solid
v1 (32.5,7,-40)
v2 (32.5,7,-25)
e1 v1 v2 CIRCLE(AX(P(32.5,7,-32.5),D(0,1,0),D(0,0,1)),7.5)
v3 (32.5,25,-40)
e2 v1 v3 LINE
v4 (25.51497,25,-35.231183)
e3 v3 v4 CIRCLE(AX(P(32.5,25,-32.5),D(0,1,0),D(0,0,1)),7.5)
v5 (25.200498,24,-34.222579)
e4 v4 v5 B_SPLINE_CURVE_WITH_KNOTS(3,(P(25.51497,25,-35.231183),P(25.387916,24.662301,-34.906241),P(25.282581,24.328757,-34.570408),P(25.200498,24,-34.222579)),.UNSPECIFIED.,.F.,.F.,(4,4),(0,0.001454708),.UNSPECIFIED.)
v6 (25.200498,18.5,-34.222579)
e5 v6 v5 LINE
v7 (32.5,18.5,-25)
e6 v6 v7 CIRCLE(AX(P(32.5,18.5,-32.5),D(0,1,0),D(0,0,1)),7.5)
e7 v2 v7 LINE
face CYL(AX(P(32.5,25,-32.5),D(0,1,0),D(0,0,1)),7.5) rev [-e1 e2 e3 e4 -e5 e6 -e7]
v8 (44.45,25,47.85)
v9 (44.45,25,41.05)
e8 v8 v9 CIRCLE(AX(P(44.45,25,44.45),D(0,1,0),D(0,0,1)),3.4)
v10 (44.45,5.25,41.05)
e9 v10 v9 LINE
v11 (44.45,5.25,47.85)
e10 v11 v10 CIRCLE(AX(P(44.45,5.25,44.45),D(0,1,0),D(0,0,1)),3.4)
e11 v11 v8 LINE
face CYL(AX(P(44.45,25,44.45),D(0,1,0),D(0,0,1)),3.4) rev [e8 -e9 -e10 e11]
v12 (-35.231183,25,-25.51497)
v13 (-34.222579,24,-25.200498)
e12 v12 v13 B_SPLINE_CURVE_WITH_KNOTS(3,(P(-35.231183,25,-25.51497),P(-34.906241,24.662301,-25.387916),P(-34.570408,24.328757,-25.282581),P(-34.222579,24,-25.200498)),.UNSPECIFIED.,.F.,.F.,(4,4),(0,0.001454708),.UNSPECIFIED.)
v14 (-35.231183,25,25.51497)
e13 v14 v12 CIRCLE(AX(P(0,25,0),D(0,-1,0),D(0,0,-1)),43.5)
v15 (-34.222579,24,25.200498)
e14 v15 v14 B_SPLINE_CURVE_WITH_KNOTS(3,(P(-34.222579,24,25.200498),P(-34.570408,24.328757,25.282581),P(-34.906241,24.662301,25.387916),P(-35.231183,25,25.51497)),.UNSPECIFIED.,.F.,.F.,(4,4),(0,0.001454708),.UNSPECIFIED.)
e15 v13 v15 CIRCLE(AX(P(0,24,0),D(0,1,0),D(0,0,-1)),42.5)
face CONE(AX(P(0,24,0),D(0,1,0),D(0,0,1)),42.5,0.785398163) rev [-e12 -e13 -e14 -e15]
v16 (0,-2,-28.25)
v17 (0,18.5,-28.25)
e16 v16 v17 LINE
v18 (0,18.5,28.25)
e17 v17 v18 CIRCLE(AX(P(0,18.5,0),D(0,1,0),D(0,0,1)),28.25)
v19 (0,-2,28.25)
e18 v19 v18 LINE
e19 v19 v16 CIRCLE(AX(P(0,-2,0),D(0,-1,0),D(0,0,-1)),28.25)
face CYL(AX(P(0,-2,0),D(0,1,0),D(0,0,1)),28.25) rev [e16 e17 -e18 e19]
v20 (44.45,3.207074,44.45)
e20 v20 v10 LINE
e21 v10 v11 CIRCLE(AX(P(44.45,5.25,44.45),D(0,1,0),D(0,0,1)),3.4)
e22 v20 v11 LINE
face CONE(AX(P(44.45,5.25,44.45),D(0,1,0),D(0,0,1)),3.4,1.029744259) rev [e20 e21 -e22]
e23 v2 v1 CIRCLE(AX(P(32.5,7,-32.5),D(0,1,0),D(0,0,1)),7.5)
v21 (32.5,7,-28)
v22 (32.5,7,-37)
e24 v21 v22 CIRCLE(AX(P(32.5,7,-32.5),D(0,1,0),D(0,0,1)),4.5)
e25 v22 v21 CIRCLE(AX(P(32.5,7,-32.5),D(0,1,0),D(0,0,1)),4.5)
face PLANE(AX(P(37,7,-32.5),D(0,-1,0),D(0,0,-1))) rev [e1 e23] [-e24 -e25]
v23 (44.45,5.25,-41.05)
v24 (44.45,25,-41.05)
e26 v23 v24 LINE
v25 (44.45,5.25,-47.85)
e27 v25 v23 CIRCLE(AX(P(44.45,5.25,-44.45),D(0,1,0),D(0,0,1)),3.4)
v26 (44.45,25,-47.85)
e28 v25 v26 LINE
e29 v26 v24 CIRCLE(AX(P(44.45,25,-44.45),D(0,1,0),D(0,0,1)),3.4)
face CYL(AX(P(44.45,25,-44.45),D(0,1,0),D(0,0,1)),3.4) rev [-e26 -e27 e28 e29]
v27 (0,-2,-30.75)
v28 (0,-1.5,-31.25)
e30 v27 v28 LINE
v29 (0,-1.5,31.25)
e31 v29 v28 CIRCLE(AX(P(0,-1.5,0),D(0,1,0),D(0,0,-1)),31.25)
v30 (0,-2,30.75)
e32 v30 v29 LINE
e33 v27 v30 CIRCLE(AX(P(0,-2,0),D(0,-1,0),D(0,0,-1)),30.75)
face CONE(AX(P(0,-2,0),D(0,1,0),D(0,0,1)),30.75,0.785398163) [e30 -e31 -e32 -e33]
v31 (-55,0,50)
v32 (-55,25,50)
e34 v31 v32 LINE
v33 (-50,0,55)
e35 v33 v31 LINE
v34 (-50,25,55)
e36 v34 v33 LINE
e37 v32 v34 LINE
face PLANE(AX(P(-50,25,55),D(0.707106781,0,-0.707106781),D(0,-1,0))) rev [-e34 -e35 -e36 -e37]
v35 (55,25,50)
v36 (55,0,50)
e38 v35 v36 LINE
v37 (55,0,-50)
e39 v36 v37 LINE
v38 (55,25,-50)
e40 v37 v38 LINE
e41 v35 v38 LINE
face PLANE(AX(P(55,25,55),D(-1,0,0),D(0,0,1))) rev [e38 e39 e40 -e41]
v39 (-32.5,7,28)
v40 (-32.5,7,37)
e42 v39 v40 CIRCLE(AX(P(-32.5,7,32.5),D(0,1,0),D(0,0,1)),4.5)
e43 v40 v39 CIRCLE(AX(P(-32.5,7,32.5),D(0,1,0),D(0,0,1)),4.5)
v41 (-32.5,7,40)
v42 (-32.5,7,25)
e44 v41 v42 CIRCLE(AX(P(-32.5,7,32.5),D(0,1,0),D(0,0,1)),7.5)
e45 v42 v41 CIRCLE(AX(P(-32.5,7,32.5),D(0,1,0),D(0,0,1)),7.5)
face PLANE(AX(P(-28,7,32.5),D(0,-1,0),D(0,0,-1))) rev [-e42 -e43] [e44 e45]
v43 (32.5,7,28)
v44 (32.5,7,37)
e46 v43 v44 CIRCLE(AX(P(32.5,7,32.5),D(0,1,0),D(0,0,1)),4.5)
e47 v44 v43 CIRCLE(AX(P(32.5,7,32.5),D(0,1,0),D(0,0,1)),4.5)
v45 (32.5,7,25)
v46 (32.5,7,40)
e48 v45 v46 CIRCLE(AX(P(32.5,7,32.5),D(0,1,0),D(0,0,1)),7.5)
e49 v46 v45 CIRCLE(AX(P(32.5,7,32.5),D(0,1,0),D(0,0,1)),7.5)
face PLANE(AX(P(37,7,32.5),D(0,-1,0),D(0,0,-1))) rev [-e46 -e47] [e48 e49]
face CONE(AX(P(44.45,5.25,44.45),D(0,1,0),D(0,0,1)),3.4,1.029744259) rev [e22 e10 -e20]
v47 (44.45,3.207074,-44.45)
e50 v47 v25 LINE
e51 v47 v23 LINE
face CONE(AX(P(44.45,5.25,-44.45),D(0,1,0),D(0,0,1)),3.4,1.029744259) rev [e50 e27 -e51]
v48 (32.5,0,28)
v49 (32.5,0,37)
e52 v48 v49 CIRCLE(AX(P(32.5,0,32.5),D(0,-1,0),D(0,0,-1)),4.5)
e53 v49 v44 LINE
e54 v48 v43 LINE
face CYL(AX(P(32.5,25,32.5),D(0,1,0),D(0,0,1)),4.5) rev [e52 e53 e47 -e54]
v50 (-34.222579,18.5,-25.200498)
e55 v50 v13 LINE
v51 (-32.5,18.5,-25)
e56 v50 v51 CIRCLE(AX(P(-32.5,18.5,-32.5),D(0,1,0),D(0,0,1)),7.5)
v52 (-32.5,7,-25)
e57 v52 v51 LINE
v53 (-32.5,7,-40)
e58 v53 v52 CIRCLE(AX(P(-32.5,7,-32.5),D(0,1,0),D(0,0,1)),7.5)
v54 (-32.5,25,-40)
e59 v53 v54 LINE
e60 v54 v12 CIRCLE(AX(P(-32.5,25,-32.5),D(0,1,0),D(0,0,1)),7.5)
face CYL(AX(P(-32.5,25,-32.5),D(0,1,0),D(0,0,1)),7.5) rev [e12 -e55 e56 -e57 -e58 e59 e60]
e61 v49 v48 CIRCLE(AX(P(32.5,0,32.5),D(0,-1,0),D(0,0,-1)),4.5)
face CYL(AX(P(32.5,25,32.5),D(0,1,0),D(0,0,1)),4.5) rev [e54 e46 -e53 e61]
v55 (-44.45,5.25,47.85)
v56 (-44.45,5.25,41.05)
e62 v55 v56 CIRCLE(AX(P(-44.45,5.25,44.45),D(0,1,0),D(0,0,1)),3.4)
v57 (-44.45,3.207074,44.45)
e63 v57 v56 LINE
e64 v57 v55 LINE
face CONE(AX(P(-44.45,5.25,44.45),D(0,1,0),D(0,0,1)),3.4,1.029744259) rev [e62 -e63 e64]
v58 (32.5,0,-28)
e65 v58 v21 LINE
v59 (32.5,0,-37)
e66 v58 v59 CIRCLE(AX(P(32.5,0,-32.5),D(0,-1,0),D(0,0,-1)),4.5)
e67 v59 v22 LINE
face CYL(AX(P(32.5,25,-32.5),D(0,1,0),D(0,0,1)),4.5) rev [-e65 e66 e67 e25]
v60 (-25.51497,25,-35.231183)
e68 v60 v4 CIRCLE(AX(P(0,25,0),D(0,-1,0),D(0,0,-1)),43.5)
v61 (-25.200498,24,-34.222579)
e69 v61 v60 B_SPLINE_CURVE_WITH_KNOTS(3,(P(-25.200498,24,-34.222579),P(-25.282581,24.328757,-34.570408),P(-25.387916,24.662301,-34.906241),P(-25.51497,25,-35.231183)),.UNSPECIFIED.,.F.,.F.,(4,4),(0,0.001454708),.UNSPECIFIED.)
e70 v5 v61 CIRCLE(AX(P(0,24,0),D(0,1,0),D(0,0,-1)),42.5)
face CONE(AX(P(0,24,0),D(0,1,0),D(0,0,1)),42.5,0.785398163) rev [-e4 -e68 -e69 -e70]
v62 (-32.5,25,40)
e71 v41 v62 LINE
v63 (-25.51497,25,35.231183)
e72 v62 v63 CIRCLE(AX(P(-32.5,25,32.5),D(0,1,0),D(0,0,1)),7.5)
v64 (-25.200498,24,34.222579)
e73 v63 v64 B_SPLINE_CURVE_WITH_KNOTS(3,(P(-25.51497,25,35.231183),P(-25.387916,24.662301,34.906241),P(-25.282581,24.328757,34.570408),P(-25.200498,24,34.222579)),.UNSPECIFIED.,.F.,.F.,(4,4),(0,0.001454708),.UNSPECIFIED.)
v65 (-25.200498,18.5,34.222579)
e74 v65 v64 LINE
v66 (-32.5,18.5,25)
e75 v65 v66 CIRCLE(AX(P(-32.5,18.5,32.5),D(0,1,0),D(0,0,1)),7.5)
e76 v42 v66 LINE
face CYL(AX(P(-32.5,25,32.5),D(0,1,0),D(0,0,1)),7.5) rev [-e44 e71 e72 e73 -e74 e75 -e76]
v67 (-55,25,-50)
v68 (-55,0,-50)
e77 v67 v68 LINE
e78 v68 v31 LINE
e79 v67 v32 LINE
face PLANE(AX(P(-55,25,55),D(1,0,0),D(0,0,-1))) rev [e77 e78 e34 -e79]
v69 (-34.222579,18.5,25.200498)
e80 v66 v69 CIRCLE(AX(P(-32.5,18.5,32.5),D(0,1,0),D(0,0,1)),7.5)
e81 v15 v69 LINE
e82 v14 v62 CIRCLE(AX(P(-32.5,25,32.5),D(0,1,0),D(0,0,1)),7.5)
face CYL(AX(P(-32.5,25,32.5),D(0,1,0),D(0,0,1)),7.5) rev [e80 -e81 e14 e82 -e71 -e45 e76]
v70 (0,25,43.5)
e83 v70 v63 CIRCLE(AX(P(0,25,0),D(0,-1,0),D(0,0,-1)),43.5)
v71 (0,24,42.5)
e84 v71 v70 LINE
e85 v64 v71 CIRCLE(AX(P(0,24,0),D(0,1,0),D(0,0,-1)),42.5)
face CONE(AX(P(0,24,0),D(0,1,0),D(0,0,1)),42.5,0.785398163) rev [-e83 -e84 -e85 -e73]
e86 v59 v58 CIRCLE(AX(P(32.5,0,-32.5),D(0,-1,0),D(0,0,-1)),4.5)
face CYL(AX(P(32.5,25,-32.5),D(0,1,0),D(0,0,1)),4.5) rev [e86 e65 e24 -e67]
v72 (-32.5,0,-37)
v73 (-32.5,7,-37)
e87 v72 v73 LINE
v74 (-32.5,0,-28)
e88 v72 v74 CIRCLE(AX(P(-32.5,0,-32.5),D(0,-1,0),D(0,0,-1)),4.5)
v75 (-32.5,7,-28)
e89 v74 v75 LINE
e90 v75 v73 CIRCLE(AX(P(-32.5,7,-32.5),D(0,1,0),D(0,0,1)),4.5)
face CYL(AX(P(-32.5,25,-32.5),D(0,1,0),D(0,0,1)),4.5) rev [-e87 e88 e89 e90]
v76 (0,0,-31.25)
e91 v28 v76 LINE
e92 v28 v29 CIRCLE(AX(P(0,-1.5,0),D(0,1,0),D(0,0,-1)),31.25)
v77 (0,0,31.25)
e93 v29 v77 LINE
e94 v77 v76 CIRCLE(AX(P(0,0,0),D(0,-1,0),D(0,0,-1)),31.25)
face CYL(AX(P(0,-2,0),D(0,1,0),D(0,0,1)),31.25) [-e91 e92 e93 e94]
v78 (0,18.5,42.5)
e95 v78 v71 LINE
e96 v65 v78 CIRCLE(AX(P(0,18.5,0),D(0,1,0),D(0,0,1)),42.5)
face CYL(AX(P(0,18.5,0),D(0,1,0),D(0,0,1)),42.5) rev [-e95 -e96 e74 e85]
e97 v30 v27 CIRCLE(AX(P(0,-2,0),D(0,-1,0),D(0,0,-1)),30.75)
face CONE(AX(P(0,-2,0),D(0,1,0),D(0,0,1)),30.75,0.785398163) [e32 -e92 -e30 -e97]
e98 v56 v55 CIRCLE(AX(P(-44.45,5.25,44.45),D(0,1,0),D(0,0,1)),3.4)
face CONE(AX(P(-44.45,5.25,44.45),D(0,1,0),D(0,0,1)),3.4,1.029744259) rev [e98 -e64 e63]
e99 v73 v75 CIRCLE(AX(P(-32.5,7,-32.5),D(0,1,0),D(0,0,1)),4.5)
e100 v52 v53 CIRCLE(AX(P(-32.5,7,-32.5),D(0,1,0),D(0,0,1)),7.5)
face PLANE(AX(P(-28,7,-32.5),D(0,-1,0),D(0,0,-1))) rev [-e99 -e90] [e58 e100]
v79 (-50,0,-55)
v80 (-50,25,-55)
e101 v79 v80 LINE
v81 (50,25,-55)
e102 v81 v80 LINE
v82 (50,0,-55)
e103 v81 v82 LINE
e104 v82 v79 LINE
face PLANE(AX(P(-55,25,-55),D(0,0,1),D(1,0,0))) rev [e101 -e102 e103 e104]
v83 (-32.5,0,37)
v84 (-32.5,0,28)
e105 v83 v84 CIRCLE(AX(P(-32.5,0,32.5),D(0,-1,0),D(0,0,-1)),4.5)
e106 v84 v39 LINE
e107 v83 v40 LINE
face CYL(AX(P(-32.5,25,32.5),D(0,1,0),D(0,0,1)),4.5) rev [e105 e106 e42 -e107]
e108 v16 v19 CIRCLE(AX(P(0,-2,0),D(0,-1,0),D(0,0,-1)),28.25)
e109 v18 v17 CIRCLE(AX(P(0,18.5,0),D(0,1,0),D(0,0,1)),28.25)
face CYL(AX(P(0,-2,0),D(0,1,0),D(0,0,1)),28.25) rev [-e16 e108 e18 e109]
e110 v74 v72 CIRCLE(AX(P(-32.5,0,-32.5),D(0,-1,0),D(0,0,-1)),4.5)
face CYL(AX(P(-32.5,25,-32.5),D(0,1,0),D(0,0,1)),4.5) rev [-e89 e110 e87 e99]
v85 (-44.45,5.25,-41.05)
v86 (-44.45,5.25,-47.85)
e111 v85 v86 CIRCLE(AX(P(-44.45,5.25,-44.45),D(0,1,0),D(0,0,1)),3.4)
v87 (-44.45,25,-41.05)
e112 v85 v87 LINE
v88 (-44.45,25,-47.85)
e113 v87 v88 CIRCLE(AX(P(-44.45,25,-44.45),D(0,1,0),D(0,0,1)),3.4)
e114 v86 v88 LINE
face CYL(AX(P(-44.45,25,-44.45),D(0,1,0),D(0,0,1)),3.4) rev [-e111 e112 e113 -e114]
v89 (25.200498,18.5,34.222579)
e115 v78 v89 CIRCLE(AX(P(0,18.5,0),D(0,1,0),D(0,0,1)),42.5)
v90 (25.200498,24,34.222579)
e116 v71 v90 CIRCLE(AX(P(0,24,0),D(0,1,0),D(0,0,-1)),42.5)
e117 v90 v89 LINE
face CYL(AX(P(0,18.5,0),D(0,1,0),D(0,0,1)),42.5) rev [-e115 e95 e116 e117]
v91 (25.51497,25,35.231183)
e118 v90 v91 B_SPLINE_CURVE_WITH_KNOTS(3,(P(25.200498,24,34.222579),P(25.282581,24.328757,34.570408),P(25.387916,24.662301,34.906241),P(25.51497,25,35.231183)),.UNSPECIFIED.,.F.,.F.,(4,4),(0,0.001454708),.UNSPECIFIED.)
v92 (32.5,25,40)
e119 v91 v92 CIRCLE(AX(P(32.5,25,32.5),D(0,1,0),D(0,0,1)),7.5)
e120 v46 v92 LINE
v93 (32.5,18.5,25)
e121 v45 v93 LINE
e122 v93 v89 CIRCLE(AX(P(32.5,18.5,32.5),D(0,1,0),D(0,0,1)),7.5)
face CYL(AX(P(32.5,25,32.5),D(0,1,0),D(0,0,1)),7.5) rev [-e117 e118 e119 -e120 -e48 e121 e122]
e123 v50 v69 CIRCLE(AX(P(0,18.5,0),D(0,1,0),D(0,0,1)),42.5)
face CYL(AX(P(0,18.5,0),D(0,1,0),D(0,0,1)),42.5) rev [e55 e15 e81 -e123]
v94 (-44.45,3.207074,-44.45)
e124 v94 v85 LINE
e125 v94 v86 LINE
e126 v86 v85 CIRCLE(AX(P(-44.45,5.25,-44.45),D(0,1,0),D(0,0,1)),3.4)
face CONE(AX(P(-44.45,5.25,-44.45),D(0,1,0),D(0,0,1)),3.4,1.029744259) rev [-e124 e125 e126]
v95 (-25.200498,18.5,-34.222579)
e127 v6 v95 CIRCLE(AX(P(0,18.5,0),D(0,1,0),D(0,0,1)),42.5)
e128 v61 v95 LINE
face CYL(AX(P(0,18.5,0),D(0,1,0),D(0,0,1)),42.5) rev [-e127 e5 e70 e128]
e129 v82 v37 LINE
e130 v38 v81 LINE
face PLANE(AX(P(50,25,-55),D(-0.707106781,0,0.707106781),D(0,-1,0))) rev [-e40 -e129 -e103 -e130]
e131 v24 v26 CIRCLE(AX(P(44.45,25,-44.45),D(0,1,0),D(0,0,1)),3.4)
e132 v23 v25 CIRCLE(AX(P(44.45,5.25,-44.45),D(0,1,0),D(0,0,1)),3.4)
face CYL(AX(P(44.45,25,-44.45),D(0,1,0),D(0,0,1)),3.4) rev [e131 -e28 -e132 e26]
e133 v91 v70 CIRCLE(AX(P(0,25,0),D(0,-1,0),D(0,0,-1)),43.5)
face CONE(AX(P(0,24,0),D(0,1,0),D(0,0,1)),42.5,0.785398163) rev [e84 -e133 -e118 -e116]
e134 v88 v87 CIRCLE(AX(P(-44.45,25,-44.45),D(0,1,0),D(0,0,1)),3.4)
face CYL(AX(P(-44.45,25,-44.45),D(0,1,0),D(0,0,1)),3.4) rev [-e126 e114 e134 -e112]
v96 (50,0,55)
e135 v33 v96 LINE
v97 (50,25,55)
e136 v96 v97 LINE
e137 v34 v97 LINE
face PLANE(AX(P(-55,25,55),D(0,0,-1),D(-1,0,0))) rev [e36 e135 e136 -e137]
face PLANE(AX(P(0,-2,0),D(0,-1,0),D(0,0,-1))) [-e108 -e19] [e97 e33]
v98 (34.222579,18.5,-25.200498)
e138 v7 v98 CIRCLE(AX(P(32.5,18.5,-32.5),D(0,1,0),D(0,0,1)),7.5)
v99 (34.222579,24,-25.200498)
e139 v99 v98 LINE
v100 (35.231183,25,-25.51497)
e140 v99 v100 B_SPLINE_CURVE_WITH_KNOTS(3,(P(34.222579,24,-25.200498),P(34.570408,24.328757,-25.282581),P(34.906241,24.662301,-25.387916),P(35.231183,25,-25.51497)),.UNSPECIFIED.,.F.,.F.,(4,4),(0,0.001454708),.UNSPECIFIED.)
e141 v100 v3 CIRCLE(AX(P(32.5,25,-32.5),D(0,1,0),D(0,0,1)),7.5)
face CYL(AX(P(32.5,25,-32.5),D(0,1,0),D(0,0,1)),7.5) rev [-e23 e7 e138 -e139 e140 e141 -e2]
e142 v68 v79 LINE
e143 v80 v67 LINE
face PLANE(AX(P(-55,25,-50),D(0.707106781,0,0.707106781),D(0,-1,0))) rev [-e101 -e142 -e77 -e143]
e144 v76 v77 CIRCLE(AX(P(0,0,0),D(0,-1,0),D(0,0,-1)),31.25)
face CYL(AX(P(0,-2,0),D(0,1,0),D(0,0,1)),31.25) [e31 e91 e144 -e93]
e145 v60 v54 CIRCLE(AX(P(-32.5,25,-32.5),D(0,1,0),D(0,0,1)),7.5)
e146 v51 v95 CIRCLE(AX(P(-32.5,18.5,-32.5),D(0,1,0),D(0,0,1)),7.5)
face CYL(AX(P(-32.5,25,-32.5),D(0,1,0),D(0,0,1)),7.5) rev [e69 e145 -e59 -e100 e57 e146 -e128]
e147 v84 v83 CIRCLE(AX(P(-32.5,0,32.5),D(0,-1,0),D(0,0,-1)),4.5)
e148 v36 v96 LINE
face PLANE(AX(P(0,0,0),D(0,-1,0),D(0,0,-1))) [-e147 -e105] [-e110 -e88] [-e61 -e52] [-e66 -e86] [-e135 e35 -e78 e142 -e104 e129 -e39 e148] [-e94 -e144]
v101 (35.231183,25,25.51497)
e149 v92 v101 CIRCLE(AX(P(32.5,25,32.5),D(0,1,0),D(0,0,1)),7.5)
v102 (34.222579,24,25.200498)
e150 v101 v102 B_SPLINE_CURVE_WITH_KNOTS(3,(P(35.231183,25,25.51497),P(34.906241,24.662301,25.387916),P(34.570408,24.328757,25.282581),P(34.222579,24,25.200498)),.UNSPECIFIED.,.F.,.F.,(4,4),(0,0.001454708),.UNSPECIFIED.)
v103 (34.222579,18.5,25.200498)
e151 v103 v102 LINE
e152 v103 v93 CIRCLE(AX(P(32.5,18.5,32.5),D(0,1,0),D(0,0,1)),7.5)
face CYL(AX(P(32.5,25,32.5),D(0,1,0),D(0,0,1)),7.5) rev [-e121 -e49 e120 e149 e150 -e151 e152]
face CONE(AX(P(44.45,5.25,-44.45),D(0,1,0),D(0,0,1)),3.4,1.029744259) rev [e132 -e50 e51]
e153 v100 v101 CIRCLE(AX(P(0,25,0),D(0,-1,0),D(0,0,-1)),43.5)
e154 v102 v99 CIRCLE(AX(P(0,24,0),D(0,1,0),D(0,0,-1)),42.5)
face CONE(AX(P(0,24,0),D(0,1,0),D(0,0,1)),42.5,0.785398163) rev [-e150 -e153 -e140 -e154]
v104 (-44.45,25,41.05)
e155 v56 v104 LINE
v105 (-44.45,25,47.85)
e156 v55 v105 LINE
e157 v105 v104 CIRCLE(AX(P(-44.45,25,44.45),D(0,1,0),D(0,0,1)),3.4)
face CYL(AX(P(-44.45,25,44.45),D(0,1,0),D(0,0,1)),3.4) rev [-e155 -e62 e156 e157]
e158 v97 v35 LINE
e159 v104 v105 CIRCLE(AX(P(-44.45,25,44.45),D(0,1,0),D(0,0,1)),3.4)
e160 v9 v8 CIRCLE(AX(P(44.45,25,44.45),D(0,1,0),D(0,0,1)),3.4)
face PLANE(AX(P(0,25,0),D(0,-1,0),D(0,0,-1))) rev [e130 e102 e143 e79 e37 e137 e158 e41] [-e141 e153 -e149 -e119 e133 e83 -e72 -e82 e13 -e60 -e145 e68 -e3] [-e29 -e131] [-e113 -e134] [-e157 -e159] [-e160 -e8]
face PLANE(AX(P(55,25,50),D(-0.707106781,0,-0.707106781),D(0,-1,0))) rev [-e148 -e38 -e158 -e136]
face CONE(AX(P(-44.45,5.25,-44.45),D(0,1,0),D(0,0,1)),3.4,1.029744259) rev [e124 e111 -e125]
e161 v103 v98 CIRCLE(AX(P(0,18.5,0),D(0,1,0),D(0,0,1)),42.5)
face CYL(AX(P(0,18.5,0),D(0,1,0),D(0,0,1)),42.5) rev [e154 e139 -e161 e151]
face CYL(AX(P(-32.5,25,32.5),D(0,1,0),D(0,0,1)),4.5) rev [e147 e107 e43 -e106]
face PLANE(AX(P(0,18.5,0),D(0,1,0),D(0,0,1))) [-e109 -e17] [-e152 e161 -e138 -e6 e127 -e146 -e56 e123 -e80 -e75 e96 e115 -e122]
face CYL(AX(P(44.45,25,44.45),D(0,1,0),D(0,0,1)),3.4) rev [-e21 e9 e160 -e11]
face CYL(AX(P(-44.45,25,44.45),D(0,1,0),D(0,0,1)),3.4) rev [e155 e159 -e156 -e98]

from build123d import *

# Parameters (mm, degrees)
SKETCH_1_W                     = 110
SKETCH_1_H                     = 110
EXTRUDE_1_DEPTH                = 25
SKETCH_3_R                     = 31.25
SKETCH_3_R_2                   = 28.25
EXTRUDE_2_DEPTH                = 2
SKETCH_4_R                     = 28.25
CUT_EXTRUDE_1_DEPTH            = 82.700673192
SKETCH_5_R                     = 42.5
CUT_EXTRUDE_2_DEPTH            = 6.5
HOLE_WIZARD_M8_1_D             = 6.8
HOLE_WIZARD_M8_1_DEPTH         = 19.75
HOLE_WIZARD_M8_1_TIP           = 2.042926105
HOLE_WIZARD_M8_1_2_D           = 9
HOLE_WIZARD_M8_1_2_CBORE_D     = 15
HOLE_WIZARD_M8_1_2_CBORE_DEPTH = 18
CHAMFER_1_SIZE                 = 5
CHAMFER_2_SIZE                 = 1
CHAMFER_3_SIZE                 = 0.5


with BuildPart() as part:
    # 草图1 → 凸台-拉伸1 (new body)
    with BuildSketch(Plane(origin=(0, 0, 0), x_dir=(1, 0, 0), z_dir=(0, 1, 0))):
        Rectangle(SKETCH_1_W, SKETCH_1_H)
    extrude(amount=EXTRUDE_1_DEPTH)

    # 草图3 → 凸台-拉伸2 (add)
    with BuildSketch(Plane.XZ):
        with Locations(Location((0, 0, 0), (0, 0, 270))):
            Circle(SKETCH_3_R)
        with Locations(Location((0, 0, 0), (0, 0, 270))):
            Circle(SKETCH_3_R_2, mode=Mode.SUBTRACT)
    extrude(amount=EXTRUDE_2_DEPTH)

    # 草图4 → 切除-拉伸1 (cut, through all)
    with BuildSketch(Plane.XZ):
        with Locations(Location((0, 0, 0), (0, 0, 270))):
            Circle(SKETCH_4_R)
    extrude(amount=-CUT_EXTRUDE_1_DEPTH, mode=Mode.SUBTRACT)

    # 草图5 → 切除-拉伸2 (cut)
    with BuildSketch(Plane(origin=(0, 25, 0), x_dir=(1, 0, 0), z_dir=(0, 1, 0))):
        with Locations(Location((0, 0, 0), (0, 0, 270))):
            Circle(SKETCH_5_R)
    extrude(amount=-CUT_EXTRUDE_2_DEPTH, mode=Mode.SUBTRACT)

    # Hole Wizard M8 _1
    with Locations(Plane(origin=(0, 25, 0), x_dir=(1, 0, 0), z_dir=(0, 1, 0))):
        with Locations((-44.45, 44.45), (0, 0), (44.45, 44.45), (-44.45, -44.45), (44.45, -44.45)):
            Hole(HOLE_WIZARD_M8_1_D / 2, depth=HOLE_WIZARD_M8_1_DEPTH)
            with Locations((0, 0, -(HOLE_WIZARD_M8_1_DEPTH + HOLE_WIZARD_M8_1_TIP / 2))):  # 118° drill point
                Cone(0, HOLE_WIZARD_M8_1_D / 2, HOLE_WIZARD_M8_1_TIP, mode=Mode.SUBTRACT)

    # Hole Wizard M8 _1 2 (through all)
    with Locations(Plane(origin=(0, 25, 0), x_dir=(1, 0, 0), z_dir=(0, 1, 0))):
        with Locations((-32.5, 32.5), (0, 0), (32.5, 32.5), (-32.5, -32.5), (32.5, -32.5)):
            CounterBoreHole(HOLE_WIZARD_M8_1_2_D / 2, HOLE_WIZARD_M8_1_2_CBORE_D / 2, HOLE_WIZARD_M8_1_2_CBORE_DEPTH)

    # 倒角1
    chamfer_1_edges = [part.edges().sort_by_distance(p)[0] for p in [
        (55, 12.5, 55),
        (-55, 12.5, 55),
        (-55, 12.5, -55),
        (55, 12.5, -55),
    ]]
    chamfer(chamfer_1_edges, length=CHAMFER_1_SIZE)

    # 倒角2
    chamfer_2_edges = [part.edges().sort_by_distance(p)[0] for p in [
        (-42.5, 25, 0),
        (42.5, 25, 0),
        (0, 25, 42.5),
        (0, 25, -42.5),
    ]]
    chamfer(chamfer_2_edges, length=CHAMFER_2_SIZE)

    # 倒角3
    chamfer_3_edges = [part.edges().sort_by_distance(p)[0] for p in [
        (0, -2, 31.25),
    ]]
    chamfer(chamfer_3_edges, length=CHAMFER_3_SIZE)


solid = part.part
